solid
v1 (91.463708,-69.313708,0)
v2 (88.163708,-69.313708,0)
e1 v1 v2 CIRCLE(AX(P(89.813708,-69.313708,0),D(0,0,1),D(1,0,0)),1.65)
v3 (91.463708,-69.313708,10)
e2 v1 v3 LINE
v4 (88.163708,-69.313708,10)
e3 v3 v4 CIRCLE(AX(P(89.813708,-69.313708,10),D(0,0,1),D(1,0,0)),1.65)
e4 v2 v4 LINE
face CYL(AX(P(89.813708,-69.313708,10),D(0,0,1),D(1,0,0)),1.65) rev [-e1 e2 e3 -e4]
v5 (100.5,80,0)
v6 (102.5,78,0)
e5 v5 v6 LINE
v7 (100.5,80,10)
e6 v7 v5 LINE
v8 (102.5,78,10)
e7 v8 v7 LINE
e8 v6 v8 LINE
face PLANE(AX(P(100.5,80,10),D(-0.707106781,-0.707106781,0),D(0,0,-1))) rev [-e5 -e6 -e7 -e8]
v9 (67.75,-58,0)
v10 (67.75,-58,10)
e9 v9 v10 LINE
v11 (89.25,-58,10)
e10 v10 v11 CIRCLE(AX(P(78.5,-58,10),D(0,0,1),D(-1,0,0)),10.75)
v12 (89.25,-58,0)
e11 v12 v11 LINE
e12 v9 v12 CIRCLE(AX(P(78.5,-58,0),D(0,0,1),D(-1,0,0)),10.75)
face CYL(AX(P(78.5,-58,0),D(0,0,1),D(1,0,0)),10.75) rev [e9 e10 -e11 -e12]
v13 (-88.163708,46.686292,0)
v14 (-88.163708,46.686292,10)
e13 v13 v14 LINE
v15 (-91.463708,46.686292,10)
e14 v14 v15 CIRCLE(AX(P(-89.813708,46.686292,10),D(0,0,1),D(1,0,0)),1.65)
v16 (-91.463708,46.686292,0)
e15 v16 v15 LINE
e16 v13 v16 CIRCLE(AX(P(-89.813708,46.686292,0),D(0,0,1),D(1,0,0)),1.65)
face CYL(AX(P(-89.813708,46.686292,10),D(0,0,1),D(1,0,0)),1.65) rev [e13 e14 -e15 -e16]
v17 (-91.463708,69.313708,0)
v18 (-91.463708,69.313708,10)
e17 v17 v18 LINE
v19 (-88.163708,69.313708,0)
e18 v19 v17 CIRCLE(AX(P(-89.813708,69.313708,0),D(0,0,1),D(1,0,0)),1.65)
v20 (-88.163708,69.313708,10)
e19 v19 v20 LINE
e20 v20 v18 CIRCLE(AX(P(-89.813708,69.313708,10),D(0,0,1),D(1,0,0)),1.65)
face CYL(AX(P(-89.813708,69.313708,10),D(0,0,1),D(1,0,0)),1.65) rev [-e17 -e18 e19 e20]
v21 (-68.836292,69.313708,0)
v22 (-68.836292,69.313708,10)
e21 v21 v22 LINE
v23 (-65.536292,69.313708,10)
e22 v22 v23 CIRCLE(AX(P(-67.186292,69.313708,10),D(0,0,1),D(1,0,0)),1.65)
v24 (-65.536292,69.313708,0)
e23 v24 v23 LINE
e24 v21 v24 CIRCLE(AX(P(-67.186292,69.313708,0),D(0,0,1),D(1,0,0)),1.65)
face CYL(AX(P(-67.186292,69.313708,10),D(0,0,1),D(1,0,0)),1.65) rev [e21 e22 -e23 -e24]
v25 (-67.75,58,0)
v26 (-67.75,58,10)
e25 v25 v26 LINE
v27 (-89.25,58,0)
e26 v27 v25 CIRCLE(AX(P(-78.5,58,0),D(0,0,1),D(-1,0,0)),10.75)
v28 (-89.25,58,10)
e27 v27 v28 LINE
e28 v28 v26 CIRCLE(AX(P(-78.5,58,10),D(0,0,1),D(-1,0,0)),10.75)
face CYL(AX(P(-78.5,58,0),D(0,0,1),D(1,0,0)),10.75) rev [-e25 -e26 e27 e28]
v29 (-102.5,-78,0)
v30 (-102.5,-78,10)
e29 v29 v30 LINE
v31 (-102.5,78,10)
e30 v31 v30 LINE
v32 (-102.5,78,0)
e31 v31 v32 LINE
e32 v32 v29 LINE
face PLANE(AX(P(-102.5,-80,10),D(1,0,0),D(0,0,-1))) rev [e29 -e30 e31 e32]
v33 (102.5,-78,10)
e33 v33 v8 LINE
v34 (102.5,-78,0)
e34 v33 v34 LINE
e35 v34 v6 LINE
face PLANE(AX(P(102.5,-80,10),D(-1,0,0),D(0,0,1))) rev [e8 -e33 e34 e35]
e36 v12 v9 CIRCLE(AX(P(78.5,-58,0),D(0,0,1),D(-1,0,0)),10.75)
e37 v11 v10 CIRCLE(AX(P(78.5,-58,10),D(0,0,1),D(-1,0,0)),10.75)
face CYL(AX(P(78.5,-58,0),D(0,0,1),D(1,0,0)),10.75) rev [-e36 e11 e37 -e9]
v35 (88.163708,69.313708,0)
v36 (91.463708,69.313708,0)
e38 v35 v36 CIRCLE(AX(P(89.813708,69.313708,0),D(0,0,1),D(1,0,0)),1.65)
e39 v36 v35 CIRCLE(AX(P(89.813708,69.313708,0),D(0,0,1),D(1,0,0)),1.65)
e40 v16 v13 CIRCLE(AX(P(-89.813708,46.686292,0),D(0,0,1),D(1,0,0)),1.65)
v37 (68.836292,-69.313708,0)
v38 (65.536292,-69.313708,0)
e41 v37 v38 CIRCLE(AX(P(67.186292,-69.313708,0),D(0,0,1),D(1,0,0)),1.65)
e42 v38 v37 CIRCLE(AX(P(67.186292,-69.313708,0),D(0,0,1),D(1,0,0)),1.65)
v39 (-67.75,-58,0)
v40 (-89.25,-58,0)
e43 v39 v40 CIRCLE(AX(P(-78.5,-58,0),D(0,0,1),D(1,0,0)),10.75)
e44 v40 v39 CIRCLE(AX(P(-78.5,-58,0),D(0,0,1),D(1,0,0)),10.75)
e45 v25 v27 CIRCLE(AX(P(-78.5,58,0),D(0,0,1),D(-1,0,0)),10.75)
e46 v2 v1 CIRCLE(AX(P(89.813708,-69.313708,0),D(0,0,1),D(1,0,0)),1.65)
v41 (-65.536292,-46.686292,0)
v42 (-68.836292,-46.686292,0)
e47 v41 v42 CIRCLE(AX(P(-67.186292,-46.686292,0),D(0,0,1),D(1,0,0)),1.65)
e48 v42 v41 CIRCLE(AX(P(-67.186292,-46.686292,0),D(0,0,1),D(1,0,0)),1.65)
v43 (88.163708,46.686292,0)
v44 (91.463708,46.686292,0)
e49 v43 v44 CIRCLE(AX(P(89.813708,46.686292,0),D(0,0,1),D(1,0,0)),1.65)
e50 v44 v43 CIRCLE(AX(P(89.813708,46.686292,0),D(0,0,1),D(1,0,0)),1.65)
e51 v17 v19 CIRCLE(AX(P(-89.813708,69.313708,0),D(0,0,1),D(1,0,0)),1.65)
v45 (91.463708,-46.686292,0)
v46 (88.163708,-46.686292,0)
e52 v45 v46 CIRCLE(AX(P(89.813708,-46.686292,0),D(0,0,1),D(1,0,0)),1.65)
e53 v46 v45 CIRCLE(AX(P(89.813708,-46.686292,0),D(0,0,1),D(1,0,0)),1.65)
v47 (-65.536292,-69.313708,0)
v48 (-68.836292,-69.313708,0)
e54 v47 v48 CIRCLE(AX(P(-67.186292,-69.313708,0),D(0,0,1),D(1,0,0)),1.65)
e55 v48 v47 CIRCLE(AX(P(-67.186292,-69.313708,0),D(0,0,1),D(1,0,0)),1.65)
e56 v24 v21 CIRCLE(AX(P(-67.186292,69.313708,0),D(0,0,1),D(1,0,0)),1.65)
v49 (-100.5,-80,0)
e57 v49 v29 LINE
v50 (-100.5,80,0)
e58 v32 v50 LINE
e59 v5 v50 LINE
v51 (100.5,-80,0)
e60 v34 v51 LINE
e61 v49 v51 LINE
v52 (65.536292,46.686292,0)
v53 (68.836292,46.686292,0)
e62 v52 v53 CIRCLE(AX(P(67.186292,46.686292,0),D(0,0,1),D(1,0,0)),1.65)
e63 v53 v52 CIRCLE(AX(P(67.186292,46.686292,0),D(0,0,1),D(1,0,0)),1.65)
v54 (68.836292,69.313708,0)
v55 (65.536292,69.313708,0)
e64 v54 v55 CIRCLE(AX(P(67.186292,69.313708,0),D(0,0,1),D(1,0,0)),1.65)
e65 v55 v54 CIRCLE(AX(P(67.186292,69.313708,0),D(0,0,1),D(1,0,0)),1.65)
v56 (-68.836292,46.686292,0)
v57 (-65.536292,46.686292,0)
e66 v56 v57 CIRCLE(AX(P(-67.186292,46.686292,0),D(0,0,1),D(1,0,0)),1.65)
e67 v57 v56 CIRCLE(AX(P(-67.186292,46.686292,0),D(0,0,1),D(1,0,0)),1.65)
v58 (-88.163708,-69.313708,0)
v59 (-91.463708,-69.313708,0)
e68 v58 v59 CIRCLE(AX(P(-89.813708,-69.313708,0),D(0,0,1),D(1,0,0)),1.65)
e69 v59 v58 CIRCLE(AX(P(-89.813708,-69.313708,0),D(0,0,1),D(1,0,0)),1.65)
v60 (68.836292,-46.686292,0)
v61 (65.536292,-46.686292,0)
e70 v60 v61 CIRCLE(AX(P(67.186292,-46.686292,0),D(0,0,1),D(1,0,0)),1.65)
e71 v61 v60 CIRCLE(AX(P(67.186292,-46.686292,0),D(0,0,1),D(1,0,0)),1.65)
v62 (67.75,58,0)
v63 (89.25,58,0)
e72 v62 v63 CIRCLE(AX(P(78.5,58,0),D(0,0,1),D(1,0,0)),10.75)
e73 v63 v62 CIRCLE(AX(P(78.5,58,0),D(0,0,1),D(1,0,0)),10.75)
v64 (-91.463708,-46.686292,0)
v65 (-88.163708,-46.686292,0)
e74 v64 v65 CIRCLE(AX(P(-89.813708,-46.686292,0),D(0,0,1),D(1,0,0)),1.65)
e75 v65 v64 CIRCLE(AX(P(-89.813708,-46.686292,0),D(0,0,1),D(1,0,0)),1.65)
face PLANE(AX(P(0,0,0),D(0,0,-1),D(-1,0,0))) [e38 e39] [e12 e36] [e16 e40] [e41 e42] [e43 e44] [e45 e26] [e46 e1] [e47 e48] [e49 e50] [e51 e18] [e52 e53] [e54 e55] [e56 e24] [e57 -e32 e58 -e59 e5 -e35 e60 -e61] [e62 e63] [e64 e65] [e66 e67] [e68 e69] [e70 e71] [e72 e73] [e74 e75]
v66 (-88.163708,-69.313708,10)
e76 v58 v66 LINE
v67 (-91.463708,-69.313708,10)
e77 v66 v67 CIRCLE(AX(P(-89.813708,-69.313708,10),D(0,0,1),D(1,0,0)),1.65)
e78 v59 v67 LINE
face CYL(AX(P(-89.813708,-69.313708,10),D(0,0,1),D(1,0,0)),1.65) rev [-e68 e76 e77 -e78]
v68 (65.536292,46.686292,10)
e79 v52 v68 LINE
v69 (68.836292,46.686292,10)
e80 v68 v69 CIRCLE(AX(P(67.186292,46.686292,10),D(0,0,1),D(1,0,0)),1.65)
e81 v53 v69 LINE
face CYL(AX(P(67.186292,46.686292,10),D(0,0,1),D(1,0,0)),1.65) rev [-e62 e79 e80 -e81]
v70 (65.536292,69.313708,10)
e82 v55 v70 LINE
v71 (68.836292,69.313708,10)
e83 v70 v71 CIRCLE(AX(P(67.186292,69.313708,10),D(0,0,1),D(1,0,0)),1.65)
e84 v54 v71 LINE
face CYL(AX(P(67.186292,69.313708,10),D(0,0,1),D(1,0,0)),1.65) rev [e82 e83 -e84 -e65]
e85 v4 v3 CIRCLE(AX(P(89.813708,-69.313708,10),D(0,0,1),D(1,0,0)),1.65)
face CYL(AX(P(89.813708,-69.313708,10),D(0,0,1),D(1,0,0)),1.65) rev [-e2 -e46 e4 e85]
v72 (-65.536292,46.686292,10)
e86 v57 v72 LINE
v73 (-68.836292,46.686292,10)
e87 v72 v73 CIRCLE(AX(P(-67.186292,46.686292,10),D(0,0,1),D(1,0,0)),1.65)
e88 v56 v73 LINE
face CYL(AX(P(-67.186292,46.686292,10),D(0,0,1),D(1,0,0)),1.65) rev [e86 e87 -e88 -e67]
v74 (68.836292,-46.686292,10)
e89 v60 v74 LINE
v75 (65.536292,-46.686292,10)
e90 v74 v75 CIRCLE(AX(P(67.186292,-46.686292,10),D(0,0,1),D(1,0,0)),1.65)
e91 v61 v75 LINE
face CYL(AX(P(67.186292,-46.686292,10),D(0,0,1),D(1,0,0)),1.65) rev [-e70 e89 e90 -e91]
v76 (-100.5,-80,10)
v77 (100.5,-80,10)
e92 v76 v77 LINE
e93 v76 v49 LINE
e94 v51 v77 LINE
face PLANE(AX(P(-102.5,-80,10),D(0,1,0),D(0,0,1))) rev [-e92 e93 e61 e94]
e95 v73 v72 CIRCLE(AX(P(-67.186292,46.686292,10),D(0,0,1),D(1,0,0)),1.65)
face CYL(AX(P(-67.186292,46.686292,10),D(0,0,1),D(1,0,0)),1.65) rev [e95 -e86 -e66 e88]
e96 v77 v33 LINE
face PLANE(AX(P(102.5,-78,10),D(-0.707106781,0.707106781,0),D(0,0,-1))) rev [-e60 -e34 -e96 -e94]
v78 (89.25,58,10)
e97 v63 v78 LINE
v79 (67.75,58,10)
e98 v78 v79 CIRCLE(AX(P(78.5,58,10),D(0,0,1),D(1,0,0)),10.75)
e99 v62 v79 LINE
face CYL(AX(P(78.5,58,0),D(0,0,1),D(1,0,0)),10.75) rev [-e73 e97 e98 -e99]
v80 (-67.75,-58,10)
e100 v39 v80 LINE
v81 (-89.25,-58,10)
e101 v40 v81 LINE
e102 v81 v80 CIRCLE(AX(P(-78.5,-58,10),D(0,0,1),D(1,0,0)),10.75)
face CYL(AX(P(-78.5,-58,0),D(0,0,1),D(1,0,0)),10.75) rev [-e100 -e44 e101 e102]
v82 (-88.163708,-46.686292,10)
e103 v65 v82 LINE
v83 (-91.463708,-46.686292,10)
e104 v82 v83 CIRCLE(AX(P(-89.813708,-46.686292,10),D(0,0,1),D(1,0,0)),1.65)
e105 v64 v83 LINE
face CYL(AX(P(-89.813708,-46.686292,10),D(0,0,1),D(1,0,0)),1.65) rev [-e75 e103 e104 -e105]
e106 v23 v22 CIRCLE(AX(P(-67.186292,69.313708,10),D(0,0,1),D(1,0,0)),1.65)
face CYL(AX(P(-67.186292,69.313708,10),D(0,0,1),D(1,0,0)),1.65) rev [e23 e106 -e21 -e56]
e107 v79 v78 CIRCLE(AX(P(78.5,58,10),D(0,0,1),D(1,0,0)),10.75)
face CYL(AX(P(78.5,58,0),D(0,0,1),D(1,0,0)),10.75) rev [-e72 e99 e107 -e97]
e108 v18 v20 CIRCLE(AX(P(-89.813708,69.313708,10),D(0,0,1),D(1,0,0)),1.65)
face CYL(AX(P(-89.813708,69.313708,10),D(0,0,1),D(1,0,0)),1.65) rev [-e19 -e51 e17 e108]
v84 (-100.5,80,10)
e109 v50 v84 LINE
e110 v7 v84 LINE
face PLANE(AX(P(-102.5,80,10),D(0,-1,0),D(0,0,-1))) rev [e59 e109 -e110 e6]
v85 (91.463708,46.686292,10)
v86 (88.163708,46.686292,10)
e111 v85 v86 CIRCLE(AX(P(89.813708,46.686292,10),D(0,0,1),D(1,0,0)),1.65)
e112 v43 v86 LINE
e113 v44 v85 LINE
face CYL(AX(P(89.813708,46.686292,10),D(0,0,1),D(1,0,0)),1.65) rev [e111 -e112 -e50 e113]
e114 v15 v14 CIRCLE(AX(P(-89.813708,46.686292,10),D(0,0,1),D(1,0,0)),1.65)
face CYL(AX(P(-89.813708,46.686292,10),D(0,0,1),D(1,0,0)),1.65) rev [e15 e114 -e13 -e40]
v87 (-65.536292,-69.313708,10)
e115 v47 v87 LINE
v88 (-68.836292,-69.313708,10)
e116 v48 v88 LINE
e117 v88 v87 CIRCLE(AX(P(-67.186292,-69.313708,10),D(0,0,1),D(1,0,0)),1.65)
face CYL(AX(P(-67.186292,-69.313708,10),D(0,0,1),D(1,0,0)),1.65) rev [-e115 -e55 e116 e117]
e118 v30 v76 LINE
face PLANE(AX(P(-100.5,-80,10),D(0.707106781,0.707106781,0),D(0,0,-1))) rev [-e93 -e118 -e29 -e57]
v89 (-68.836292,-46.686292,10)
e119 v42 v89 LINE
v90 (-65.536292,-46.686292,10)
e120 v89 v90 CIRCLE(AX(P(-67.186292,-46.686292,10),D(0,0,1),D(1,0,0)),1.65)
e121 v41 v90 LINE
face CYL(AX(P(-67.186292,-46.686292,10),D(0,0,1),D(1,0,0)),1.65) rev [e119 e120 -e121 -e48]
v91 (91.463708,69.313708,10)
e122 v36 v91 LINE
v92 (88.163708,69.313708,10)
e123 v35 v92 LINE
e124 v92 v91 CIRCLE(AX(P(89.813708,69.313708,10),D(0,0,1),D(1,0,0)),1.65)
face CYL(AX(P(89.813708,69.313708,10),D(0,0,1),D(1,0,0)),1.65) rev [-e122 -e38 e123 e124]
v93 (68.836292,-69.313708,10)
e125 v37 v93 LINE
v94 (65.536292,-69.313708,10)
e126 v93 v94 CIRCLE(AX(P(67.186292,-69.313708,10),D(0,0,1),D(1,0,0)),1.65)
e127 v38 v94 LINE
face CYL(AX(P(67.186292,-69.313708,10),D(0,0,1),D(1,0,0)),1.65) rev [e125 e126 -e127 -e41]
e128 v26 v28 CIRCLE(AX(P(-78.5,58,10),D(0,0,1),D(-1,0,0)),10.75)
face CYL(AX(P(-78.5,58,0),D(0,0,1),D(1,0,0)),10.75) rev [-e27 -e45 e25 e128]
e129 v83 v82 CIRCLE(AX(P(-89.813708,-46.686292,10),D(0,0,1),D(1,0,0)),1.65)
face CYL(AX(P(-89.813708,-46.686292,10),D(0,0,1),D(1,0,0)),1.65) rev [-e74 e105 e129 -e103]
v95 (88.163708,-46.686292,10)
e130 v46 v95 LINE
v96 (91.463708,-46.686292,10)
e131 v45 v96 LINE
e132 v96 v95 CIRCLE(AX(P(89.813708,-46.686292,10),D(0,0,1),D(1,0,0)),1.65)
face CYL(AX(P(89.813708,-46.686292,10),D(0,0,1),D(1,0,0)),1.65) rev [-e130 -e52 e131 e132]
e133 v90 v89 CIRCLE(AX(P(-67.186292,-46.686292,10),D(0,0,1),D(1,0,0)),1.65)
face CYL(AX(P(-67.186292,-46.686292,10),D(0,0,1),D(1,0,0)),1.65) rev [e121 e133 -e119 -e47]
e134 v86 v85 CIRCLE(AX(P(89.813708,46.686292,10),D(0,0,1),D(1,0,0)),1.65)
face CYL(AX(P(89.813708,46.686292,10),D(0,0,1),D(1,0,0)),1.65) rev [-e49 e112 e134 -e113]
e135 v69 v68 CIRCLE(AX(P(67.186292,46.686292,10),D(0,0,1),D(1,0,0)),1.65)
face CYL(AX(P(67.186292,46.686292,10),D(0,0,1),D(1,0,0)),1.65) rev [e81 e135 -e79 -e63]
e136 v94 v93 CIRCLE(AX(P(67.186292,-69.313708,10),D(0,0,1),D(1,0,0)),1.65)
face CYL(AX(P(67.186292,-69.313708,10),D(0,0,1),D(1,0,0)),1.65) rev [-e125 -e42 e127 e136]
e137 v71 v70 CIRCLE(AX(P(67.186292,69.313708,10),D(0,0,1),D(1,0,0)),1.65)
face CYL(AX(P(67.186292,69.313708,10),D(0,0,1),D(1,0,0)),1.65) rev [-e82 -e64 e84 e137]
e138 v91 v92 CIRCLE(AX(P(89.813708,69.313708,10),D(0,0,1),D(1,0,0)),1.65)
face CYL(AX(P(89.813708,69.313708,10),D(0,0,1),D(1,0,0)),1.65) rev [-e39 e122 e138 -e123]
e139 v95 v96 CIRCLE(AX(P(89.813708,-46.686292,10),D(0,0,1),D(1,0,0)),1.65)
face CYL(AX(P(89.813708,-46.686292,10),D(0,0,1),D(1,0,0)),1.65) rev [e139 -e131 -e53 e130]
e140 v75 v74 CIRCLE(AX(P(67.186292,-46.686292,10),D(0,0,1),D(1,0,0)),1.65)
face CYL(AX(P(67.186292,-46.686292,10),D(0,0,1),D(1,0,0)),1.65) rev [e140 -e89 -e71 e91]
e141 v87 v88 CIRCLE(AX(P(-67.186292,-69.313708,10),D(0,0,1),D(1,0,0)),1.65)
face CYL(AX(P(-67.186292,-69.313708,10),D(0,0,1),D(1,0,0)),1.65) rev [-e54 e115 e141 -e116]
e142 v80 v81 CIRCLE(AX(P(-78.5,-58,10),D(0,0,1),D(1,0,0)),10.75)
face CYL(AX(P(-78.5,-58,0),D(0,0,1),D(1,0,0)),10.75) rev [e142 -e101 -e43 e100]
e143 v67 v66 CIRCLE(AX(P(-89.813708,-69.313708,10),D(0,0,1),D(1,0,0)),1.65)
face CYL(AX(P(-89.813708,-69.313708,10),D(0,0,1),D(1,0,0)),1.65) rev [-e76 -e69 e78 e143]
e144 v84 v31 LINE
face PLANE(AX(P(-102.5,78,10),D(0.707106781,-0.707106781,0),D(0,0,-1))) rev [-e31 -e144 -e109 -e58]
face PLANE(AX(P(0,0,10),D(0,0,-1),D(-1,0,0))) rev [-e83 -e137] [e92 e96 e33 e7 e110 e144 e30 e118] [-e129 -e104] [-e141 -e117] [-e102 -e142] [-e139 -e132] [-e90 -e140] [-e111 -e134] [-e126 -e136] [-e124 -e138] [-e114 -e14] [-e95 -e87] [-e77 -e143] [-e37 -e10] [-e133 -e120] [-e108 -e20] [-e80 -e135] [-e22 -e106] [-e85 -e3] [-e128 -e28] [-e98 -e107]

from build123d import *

# Parameters (mm, degrees)
SKETCH1_W           = 205
SKETCH1_H           = 160
BOSS_EXTRUDE1_DEPTH = 10
SKETCH2_R           = 10.75
CUT_EXTRUDE1_DEPTH  = 131.408013557
M4_TAPPED_HOLE1_D   = 3.3
CHAMFER1_SIZE       = 2


with BuildPart() as part:
    # Sketch1 → Boss-Extrude1 (new body)
    with BuildSketch(Plane.XY):
        Rectangle(SKETCH1_W, SKETCH1_H)
    extrude(amount=BOSS_EXTRUDE1_DEPTH)

    # Sketch2 → Cut-Extrude1 (cut, through all)
    with BuildSketch(Plane.XY.offset(10)):
        with Locations((-78.5, -58)):
            Circle(SKETCH2_R)
        with Locations(Location((-78.5, 58, 0), (0, 0, 180))):
            Circle(SKETCH2_R)
        with Locations(Location((78.5, -58, 0), (0, 0, 180))):
            Circle(SKETCH2_R)
        with Locations((78.5, 58)):
            Circle(SKETCH2_R)
    extrude(amount=-CUT_EXTRUDE1_DEPTH, mode=Mode.SUBTRACT)

    # M4 Tapped Hole1 (through all)
    with Locations(Plane.XY.offset(10)):
        with Locations((-89.813708499, 69.313708499), (-67.186291501, 69.313708499), (-67.186291501, 46.686291501), (-89.813708499, 46.686291501), (67.186291501, 69.313708499), (89.813708499, 69.313708499), (67.186291501, 46.686291501), (89.813708499, 46.686291501), (-89.813708499, -46.686291501), (-67.186291501, -46.686291501), (-89.813708499, -69.313708499), (-67.186291501, -69.313708499), (67.186291501, -46.686291501), (89.813708499, -46.686291501), (67.186291501, -69.313708499), (89.813708499, -69.313708499)):
            Hole(M4_TAPPED_HOLE1_D / 2)

    # Chamfer1
    chamfer1_edges = [part.edges().sort_by_distance(p)[0] for p in [
        (102.5, -80, 5),
        (-102.5, -80, 5),
        (-102.5, 80, 5),
        (102.5, 80, 5),
    ]]
    chamfer(chamfer1_edges, length=CHAMFER1_SIZE)


solid = part.part
